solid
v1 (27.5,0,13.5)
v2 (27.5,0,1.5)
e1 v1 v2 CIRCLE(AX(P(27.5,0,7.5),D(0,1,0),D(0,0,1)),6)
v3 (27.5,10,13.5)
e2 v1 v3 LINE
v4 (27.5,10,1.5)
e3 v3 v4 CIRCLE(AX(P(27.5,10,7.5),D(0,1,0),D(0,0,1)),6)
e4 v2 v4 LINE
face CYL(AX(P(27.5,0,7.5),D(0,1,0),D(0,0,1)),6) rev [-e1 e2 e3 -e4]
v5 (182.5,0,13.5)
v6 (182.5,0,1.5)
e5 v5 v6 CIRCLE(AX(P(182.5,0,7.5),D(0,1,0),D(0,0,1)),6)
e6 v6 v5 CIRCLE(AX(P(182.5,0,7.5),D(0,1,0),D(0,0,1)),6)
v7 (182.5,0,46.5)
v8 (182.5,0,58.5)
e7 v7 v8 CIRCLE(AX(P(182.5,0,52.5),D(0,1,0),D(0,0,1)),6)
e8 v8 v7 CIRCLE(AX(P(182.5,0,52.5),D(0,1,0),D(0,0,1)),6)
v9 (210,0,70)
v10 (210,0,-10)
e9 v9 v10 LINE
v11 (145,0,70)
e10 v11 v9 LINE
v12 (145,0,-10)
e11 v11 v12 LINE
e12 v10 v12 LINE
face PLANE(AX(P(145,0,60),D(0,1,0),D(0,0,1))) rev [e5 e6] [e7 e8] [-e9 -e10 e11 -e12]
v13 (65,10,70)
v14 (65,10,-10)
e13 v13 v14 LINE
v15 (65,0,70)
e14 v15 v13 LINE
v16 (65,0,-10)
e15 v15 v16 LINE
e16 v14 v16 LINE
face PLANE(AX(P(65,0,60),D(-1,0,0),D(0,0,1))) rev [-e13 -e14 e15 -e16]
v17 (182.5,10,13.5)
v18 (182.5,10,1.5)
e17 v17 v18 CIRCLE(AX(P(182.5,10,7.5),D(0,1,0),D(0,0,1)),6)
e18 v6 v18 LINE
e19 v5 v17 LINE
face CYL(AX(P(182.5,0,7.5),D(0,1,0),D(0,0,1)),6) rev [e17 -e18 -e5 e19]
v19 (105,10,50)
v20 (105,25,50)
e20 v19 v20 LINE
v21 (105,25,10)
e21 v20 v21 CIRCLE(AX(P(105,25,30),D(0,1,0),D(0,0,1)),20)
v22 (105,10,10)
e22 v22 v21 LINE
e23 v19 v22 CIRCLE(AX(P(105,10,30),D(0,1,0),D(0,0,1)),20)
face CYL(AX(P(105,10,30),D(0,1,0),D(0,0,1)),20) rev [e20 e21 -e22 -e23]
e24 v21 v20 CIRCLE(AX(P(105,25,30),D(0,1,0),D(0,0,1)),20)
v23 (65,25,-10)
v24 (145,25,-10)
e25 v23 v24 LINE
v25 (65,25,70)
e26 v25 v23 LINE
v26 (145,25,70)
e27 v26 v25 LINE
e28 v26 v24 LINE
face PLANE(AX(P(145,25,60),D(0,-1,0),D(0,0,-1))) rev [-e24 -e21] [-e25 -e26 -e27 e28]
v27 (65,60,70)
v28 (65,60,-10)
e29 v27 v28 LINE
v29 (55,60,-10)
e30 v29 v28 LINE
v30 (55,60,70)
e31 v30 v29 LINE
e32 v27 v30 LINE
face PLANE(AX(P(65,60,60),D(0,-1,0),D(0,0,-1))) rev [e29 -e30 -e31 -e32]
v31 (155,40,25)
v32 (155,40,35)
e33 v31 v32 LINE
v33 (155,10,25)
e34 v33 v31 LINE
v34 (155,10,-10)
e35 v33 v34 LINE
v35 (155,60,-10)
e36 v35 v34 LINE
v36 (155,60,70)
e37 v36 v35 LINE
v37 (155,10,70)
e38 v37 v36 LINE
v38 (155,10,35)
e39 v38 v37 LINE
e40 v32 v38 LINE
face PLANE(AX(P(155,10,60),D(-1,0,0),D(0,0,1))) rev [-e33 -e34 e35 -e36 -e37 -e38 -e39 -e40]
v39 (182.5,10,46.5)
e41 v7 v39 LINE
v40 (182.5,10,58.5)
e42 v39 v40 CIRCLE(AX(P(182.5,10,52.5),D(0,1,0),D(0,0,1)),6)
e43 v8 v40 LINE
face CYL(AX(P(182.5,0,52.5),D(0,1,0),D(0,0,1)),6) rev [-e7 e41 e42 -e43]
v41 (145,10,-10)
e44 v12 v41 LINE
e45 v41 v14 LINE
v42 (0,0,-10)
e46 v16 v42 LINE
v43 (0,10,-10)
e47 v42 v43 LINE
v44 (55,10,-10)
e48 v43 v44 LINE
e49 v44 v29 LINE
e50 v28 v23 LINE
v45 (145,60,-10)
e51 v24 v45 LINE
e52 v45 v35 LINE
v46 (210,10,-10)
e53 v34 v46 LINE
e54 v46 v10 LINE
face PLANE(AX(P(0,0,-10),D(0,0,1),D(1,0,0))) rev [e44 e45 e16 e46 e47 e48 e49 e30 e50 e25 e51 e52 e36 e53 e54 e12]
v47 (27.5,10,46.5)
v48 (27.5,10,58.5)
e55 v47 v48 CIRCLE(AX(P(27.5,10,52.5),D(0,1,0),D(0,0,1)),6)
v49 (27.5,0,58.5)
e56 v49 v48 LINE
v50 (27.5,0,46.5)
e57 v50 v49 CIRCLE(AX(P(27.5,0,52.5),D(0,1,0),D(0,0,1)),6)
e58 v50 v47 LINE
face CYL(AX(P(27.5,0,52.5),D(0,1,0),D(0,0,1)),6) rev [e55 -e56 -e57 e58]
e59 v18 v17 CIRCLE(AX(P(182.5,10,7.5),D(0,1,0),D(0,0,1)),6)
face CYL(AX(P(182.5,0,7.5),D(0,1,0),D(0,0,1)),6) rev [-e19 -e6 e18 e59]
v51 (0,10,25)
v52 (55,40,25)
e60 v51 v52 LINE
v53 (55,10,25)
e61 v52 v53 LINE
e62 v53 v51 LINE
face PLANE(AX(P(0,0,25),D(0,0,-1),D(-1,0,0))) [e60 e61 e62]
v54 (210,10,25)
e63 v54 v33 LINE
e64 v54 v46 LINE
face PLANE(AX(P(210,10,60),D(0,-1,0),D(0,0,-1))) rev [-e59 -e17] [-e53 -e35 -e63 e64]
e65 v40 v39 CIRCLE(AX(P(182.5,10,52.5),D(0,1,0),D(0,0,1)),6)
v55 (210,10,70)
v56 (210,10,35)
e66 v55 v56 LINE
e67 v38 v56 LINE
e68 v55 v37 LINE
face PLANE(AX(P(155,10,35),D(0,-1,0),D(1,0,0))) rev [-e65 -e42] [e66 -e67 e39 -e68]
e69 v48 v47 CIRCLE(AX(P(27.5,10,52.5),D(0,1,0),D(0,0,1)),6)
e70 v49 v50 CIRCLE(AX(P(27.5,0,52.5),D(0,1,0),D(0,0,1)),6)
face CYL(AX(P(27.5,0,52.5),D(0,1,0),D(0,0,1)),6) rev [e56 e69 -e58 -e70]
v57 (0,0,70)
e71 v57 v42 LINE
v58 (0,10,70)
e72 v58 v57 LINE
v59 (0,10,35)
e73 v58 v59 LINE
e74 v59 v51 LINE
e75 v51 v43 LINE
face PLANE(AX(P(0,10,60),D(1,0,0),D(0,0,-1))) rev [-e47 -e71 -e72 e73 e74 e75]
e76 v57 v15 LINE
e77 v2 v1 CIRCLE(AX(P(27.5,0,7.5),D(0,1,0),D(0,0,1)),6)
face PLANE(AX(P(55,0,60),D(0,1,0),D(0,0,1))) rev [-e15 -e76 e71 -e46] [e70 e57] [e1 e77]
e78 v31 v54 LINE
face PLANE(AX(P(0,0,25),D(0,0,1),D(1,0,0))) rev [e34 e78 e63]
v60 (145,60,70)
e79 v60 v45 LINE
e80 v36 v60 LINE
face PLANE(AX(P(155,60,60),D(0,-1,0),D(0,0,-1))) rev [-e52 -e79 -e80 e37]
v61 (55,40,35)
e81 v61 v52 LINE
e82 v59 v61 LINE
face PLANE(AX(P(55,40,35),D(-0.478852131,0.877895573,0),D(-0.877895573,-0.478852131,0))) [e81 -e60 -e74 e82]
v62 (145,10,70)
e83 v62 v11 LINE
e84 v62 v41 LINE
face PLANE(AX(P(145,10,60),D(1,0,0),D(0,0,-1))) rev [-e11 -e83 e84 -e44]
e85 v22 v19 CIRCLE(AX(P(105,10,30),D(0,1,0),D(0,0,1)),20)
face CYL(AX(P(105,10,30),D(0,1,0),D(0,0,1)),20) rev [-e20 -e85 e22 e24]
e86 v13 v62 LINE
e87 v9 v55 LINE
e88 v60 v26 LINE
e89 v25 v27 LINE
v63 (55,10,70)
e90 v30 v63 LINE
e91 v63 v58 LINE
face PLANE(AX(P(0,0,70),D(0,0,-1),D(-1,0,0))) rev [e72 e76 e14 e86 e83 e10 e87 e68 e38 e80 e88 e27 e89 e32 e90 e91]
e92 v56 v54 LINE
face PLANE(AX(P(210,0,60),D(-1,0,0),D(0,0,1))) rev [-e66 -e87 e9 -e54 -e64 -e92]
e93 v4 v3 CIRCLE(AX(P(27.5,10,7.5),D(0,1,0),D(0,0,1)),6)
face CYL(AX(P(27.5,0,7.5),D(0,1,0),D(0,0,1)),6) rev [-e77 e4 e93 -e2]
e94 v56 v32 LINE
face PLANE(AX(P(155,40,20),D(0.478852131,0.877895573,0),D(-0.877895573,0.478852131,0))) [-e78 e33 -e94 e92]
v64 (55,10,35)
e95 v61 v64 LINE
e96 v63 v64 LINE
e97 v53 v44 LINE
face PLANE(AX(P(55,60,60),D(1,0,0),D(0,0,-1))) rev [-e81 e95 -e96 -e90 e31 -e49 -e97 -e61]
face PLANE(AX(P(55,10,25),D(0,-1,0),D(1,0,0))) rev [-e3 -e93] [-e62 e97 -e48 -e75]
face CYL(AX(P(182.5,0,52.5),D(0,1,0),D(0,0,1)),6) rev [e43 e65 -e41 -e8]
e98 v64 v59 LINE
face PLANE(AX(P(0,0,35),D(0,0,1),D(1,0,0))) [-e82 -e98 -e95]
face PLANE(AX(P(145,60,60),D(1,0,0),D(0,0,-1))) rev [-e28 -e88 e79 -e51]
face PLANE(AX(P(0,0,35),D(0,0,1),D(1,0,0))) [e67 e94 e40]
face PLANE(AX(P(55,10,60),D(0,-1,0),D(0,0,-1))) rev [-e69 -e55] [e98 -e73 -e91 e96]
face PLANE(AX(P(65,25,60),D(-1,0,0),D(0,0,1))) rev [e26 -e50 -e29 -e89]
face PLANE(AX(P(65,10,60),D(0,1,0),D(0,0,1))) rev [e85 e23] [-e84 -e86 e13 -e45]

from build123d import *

# Parameters (mm, degrees)
BASE_BODY_DEPTH          = 60
CENTER_BORE_SKETCH_R     = 20
CENTER_BORE_DEPTH        = 15
GUSSET_1_BLANK_DEPTH     = 40
GUSSET_1_TRIM_A_DEPTH    = 25
GUSSET_1_TRIM_B_DEPTH    = 5
GUSSET_2_BLANK_DEPTH     = 35
GUSSET_2_TRIM_DEPTH      = 25
FLANGE_EXTENSION_1_DEPTH = 10
FLANGE_EXTENSION_2_DEPTH = 10
MOUNTING_HOLES_SKETCH_R  = 6
MOUNTING_HOLES_4X_DEPTH  = 10


with BuildPart() as part:
    # Base Profile Sketch → Base Body (new body)
    with BuildSketch(Plane.XY):
        Polygon((0, 0), (55, 0), (65, 0), (65, 10), (145, 10), (145, 0), (210, 0), (210, 10), (155, 10), (155, 60), (145, 60), (145, 25), (65, 25), (65, 60), (55, 60), (55, 10), (0, 10), align=None)
    extrude(amount=BASE_BODY_DEPTH)

    # Center Bore Sketch → Center Bore (cut)
    with BuildSketch(Plane(origin=(0, 25, 0), x_dir=(1, 0, 0), z_dir=(0, 1, 0))):
        with Locations(Location((105, -30, 0), (0, 0, 270))):
            Circle(CENTER_BORE_SKETCH_R)
    extrude(amount=-CENTER_BORE_DEPTH, mode=Mode.SUBTRACT)

    # Gusset 1 Sketch → Gusset 1 Blank (add)
    with BuildSketch(Plane.XY.offset(60)):
        Polygon((155, 10), (155, 40), (210, 10), align=None)
    extrude(amount=-GUSSET_1_BLANK_DEPTH)

    # Gusset 1 Trim A Sketch → Gusset 1 Trim A (cut)
    with BuildSketch(Plane.XY.offset(60)):
        Polygon((155, 40), (155, 10), (210, 10), align=None)
    extrude(amount=-GUSSET_1_TRIM_A_DEPTH, mode=Mode.SUBTRACT)

    # Gusset 1 Trim B Sketch → Gusset 1 Trim B (cut)
    with BuildSketch(Plane(origin=(0, 0, 20), x_dir=(-1, 0, 0), z_dir=(0, 0, -1))):
        Polygon((-210, 10), (-155, 10), (-155, 40), align=None)
    extrude(amount=-GUSSET_1_TRIM_B_DEPTH, mode=Mode.SUBTRACT)

    # Gusset 2 Sketch → Gusset 2 Blank (add)
    with BuildSketch(Plane(origin=(0, 0, 0), x_dir=(-1, 0, 0), z_dir=(0, 0, -1))):
        Polygon((-55, 10), (-55, 40), (0, 10), align=None)
    extrude(amount=-GUSSET_2_BLANK_DEPTH)

    # Gusset 2 Trim Sketch → Gusset 2 Trim (cut)
    with BuildSketch(Plane(origin=(0, 0, 0), x_dir=(-1, 0, 0), z_dir=(0, 0, -1))):
        Polygon((-55, 40), (-55, 10), (0, 10), align=None)
    extrude(amount=-GUSSET_2_TRIM_DEPTH, mode=Mode.SUBTRACT)

    # Flange Extension 1 Sketch → Flange Extension 1 (add)
    with BuildSketch(Plane.XY.offset(60)):
        Polygon((0, 0), (0, 10), (55, 10), (55, 60), (65, 60), (65, 25), (145, 25), (145, 60), (155, 60), (155, 10), (210, 10), (210, 0), (145, 0), (145, 10), (65, 10), (65, 0), align=None)
    extrude(amount=FLANGE_EXTENSION_1_DEPTH)

    # Flange Extension 2 Sketch → Flange Extension 2 (add)
    with BuildSketch(Plane(origin=(0, 0, 0), x_dir=(-1, 0, 0), z_dir=(0, 0, -1))):
        Polygon((-210, 0), (-210, 10), (-155, 10), (-155, 60), (-145, 60), (-145, 25), (-65, 25), (-65, 60), (-55, 60), (-55, 10), (0, 10), (0, 0), (-65, 0), (-65, 10), (-145, 10), (-145, 0), align=None)
    extrude(amount=FLANGE_EXTENSION_2_DEPTH)

    # Mounting Holes Sketch → Mounting Holes 4x (cut)
    with BuildSketch(Plane(origin=(0, 10, 0), x_dir=(1, 0, 0), z_dir=(0, 1, 0))):
        with Locations(Location((27.5, -52.5, 0), (0, 0, 270))):
            Circle(MOUNTING_HOLES_SKETCH_R)
        with Locations(Location((27.5, -7.5, 0), (0, 0, 270))):
            Circle(MOUNTING_HOLES_SKETCH_R)
        with Locations(Location((182.5, -7.5, 0), (0, 0, 270))):
            Circle(MOUNTING_HOLES_SKETCH_R)
        with Locations(Location((182.5, -52.5, 0), (0, 0, 270))):
            Circle(MOUNTING_HOLES_SKETCH_R)
    extrude(amount=-MOUNTING_HOLES_4X_DEPTH, mode=Mode.SUBTRACT)


solid = part.part
